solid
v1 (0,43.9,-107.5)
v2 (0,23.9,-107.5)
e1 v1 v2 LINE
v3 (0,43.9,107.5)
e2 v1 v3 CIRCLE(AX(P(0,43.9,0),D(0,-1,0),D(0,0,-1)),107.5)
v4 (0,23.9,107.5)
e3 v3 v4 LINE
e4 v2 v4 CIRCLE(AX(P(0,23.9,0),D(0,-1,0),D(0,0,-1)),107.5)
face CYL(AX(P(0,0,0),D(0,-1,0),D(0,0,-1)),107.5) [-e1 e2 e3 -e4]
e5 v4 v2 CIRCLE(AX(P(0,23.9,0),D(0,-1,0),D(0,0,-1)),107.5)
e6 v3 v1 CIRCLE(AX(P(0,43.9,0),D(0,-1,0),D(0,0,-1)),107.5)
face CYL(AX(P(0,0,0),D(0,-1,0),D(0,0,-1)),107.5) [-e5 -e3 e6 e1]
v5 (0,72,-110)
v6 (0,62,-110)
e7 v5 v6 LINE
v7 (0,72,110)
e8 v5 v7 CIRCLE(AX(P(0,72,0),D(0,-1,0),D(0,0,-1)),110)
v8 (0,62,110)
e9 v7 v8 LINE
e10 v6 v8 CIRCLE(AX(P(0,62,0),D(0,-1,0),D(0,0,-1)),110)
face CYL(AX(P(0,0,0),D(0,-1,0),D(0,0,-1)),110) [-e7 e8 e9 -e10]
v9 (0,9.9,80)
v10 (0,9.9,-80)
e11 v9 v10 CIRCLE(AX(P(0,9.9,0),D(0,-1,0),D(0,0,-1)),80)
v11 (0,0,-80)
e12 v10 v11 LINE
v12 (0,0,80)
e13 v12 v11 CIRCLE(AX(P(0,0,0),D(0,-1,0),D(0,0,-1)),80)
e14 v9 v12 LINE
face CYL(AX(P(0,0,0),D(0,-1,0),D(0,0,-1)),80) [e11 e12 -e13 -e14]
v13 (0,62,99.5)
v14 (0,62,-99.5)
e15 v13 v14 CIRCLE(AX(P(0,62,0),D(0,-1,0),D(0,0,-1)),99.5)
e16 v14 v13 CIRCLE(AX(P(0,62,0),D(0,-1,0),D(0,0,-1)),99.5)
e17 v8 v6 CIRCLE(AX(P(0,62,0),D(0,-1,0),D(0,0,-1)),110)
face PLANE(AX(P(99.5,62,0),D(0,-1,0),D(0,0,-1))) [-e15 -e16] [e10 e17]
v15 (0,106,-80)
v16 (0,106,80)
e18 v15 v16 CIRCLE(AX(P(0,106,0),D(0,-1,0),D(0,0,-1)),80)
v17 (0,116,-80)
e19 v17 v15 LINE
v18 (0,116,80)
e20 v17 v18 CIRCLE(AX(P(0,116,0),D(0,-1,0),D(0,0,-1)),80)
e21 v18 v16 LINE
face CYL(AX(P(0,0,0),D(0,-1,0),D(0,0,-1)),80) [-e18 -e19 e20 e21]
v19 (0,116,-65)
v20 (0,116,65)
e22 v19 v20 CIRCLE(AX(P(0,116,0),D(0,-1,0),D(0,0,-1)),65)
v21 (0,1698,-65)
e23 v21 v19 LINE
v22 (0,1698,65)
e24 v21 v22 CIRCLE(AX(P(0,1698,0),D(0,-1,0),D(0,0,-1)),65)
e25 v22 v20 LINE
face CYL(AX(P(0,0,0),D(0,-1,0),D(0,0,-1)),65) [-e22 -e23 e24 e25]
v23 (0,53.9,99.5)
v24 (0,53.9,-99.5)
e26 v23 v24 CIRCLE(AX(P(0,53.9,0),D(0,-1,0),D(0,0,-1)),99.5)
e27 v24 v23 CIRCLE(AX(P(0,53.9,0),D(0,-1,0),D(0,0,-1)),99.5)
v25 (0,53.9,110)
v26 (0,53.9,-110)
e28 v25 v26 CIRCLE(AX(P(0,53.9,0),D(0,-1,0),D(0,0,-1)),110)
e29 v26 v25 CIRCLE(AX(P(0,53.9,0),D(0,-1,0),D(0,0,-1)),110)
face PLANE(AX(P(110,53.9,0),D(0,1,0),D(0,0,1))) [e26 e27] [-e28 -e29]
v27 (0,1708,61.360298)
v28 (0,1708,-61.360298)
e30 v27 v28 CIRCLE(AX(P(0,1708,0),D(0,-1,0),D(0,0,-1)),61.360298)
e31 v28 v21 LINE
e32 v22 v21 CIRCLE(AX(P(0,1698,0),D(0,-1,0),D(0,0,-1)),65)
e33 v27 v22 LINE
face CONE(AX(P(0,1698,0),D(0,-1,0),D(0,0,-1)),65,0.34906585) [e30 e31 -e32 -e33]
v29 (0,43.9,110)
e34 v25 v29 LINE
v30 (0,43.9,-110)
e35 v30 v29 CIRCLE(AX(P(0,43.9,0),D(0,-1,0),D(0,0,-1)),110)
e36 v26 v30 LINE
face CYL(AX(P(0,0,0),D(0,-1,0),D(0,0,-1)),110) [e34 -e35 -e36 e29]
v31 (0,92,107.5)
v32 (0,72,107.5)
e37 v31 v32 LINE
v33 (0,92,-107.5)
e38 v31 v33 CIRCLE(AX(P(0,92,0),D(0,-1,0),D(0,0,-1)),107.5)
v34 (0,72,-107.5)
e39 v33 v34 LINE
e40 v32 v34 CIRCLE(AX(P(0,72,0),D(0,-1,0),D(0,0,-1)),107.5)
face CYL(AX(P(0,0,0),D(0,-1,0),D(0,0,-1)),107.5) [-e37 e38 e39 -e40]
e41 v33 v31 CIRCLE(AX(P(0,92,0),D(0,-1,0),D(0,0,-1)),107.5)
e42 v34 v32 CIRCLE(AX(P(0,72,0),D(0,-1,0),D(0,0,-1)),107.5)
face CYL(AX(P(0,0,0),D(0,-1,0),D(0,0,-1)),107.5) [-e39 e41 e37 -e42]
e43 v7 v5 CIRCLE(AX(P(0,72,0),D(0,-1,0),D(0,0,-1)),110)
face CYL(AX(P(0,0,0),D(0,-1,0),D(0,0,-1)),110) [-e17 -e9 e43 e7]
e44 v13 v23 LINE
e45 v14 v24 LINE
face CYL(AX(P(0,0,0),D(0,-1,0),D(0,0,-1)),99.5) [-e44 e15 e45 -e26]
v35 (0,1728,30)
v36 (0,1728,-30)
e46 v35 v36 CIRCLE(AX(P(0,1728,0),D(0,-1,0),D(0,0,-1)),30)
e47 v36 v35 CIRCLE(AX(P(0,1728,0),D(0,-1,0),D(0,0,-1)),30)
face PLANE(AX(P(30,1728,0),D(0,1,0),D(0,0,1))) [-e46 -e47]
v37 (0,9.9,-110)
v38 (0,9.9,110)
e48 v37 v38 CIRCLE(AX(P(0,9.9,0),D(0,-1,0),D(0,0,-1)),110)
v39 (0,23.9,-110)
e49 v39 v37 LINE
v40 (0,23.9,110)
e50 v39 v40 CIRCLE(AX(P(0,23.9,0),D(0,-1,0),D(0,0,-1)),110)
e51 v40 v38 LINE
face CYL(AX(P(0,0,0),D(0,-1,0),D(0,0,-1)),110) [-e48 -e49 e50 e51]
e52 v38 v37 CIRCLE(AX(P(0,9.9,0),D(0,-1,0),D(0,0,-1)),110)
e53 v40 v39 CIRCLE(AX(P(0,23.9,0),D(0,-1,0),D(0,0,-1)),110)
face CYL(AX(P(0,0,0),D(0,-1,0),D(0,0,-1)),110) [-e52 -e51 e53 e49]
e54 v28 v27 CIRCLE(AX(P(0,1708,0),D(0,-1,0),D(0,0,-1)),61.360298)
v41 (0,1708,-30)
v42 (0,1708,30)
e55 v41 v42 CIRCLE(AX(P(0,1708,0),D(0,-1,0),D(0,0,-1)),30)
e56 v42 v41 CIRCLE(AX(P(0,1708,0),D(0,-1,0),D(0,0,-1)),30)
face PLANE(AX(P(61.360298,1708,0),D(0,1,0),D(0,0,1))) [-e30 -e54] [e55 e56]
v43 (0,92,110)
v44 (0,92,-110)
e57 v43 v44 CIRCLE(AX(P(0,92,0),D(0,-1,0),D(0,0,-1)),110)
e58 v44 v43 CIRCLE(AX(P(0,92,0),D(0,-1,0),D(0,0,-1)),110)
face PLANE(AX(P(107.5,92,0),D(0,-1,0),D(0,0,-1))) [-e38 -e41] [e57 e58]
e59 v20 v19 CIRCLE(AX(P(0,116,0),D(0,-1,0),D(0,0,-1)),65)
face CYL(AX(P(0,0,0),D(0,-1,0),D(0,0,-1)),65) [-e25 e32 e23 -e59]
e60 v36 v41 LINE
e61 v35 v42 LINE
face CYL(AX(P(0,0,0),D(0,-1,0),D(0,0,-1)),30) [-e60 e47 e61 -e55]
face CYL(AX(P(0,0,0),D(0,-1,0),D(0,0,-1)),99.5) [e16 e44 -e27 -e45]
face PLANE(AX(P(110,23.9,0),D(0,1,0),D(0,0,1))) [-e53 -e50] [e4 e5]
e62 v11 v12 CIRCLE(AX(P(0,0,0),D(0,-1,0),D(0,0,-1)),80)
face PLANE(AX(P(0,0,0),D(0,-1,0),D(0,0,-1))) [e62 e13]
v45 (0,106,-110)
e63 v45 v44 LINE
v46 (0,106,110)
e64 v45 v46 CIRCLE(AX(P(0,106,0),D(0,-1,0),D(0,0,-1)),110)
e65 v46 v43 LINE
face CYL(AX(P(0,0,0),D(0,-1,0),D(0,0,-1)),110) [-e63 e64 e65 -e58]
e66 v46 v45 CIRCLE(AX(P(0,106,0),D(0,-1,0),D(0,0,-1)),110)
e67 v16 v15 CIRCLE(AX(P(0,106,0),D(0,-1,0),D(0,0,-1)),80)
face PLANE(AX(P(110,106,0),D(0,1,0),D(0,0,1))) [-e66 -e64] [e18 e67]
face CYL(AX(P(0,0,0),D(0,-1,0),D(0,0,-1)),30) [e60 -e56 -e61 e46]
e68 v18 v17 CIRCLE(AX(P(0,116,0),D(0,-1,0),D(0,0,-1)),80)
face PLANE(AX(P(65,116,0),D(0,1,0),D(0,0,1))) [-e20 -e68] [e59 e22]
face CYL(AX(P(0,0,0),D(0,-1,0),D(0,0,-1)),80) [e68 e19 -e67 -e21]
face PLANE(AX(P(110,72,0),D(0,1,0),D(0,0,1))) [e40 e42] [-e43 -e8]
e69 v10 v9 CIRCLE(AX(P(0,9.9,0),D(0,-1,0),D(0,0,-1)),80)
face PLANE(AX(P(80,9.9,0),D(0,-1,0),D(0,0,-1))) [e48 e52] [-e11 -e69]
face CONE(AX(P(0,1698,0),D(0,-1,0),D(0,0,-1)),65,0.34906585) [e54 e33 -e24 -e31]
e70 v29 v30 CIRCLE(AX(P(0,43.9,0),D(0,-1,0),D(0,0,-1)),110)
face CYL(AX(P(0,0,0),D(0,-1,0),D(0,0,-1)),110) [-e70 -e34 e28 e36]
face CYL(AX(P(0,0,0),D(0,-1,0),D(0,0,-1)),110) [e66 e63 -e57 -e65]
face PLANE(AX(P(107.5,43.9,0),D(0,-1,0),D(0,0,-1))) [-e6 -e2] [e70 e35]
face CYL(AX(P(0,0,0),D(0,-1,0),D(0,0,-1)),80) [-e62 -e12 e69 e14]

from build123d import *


with BuildPart() as part:
    # Sketch1 → Revolve1 (revolve)
    with BuildSketch(Plane.XY, mode=Mode.PRIVATE) as revolve1_sk:
        Polygon((0, 0), (80, 0), (80, 9.9), (110, 9.9), (110, 23.9), (107.5, 23.9), (107.5, 43.9), (110, 43.9), (110, 53.9), (99.5, 53.9), (99.5, 62), (110, 62), (110, 72), (107.5, 72), (107.5, 92), (110, 92), (110, 106), (80, 106), (80, 116), (65, 116), (65, 1698), (61.360297657, 1708), (30, 1708), (30, 1728), (0, 1728), align=None)
    revolve(revolve1_sk.sketch.rotate(Axis((0, 0, 0), (0, 1, 0)), 90), axis=Axis((0, 0, 0), (0, 1, 0)))


solid = part.part
